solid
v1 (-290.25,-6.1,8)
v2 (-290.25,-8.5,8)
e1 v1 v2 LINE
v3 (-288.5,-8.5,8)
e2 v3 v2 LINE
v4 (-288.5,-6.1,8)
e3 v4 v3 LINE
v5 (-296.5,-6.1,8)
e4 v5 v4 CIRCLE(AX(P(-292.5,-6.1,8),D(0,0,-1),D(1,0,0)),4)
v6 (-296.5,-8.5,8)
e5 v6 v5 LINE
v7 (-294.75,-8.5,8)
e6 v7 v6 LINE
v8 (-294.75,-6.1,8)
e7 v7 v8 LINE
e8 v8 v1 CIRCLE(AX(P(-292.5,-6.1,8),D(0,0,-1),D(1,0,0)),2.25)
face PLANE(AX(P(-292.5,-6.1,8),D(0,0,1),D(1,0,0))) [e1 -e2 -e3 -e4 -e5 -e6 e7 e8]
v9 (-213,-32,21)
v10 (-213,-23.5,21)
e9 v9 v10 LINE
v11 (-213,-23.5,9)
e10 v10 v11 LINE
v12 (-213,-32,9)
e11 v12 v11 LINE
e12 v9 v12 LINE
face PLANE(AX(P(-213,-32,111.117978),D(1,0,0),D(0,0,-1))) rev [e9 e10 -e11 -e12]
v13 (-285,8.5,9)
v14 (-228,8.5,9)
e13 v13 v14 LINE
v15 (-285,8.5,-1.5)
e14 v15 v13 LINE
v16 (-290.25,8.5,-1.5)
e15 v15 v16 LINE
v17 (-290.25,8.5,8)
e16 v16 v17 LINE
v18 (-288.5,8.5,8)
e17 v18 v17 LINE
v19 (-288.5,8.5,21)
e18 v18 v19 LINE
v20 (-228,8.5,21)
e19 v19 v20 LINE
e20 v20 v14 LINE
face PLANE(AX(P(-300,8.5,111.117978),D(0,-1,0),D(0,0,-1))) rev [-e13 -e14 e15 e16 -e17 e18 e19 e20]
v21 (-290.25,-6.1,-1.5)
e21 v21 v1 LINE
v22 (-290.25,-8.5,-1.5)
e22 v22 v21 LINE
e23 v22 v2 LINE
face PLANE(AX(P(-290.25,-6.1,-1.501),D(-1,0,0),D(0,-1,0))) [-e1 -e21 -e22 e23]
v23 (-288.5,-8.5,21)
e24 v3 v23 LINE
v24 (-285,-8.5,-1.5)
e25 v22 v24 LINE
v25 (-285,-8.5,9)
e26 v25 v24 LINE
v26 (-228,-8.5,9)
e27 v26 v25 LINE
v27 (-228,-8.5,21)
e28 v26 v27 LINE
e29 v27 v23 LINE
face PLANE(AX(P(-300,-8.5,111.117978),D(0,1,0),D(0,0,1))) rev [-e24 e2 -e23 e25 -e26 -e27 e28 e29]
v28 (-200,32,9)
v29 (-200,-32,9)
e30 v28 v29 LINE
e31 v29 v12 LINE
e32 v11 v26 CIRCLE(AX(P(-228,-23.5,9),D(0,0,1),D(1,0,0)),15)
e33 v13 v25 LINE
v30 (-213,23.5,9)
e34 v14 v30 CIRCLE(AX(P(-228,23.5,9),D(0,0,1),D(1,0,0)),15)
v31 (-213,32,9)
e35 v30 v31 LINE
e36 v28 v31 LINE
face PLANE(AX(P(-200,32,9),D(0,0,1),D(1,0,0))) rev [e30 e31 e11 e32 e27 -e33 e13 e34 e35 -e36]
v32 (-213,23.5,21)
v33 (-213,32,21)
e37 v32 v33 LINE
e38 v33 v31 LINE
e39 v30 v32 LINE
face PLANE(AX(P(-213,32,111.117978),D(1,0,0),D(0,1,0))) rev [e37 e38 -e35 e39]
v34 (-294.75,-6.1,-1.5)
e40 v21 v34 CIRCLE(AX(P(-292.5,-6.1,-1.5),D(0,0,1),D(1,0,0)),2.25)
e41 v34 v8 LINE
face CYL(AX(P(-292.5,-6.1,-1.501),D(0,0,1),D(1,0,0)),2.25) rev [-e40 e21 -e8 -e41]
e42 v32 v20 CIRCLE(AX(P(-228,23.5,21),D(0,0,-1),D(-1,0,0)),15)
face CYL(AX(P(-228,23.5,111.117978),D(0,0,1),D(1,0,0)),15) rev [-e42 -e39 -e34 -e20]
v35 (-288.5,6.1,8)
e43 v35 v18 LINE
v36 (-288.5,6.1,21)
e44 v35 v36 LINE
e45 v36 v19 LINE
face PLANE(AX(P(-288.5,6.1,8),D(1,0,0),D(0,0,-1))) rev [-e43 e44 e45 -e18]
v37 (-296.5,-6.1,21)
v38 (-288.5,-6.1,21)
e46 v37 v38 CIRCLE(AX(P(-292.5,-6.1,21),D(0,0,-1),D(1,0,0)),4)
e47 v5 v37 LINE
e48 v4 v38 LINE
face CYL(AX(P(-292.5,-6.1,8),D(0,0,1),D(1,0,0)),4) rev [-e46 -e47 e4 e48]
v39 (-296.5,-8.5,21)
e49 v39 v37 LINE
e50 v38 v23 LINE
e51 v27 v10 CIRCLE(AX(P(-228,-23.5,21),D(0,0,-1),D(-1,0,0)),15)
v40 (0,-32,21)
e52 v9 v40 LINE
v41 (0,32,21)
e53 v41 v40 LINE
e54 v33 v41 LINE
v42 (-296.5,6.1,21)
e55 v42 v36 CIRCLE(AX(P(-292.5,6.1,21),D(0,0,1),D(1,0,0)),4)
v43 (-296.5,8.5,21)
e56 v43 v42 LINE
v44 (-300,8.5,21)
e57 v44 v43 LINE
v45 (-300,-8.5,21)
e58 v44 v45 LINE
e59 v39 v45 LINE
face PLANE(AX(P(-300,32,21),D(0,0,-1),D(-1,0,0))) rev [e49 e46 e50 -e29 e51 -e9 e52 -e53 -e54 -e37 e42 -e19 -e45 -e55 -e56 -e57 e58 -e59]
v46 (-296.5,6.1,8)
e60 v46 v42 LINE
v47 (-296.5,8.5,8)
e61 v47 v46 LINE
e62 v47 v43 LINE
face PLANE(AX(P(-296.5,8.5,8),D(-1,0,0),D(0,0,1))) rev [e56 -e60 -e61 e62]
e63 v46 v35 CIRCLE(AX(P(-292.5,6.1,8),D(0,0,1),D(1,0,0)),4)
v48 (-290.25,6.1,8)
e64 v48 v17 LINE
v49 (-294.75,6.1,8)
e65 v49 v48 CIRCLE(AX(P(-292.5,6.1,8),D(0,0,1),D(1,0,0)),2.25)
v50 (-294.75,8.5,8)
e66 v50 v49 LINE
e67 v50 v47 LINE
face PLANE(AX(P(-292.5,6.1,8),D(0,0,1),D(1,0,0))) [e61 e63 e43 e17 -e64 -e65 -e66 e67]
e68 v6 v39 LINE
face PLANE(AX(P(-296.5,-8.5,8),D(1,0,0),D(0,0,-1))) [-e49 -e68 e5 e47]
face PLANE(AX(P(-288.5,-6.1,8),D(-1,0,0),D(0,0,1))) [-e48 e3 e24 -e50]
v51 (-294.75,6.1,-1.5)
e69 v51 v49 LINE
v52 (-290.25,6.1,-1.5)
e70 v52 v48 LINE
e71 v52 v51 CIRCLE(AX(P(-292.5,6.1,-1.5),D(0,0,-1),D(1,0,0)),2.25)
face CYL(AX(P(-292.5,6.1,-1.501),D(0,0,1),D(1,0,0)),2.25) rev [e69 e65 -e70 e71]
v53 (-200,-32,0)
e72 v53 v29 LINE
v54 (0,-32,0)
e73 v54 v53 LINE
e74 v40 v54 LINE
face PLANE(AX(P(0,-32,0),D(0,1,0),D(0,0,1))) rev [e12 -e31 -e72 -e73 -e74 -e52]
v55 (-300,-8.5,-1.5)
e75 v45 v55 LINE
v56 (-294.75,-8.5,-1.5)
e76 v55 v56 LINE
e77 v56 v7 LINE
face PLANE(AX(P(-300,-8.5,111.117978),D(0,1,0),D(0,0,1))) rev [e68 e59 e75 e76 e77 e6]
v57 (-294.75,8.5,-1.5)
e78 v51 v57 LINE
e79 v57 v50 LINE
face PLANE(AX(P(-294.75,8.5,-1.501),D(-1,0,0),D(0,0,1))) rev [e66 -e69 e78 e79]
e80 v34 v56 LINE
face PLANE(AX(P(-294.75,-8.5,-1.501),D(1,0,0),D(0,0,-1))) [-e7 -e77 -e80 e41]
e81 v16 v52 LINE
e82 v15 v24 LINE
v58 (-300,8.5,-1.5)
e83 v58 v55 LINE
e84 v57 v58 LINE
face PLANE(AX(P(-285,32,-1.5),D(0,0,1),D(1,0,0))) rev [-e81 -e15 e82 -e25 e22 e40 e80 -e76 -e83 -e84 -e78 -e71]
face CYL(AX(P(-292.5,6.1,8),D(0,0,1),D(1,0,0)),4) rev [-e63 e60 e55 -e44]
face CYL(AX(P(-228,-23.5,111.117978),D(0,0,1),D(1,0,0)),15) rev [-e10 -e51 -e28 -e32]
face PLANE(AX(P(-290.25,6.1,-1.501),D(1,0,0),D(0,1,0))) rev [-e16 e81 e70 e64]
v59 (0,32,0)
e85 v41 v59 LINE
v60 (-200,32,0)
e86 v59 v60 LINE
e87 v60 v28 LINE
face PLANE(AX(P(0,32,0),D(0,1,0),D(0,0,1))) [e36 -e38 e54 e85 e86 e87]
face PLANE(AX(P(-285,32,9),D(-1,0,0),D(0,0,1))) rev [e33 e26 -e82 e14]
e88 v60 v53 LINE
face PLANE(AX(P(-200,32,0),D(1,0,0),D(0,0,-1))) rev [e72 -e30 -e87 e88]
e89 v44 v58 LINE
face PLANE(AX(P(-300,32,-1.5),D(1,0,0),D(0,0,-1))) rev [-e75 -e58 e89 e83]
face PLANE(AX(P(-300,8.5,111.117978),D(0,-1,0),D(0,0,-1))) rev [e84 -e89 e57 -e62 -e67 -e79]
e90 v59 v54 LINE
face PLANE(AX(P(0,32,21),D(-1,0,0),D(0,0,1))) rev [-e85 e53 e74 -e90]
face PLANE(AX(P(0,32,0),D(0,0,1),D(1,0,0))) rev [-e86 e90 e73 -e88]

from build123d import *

# Parameters (mm, degrees)
EXTRUDE_1_DEPTH     = 32
SKETCH_2_W          = 87
SKETCH_2_H          = 23.5
CUT_EXTRUDE_1_DEPTH = 22.5
FILLET_1_R          = 15
CUT_EXTRUDE_2_DEPTH = 13
CUT_EXTRUDE_3_REACH = 303.982


with BuildPart() as part:
    # 草图1 → 凸台-拉伸1 (new, symmetric)
    with BuildSketch(Plane(origin=(0, 0, 0), x_dir=(1, 0, 0), z_dir=(0, 1, 0))):
        Polygon((0, 0), (-200, 0), (-200, -9), (-285, -9), (-285, 1.5), (-300, 1.5), (-300, -21), (0, -21), align=None)
    extrude(amount=EXTRUDE_1_DEPTH, both=True)

    # 草图2 → 切除-拉伸1 (cut)
    with BuildSketch(Plane(origin=(0, 0, -1.5), x_dir=(-1, 0, 0), z_dir=(0, 0, -1))):
        with Locations((256.5, -20.25)):
            Rectangle(SKETCH_2_W, SKETCH_2_H)
        with Locations((256.5, 20.25)):
            Rectangle(SKETCH_2_W, SKETCH_2_H)
    extrude(amount=-CUT_EXTRUDE_1_DEPTH, mode=Mode.SUBTRACT)

    # 圆角1
    fillet_1_edges = [part.edges().sort_by_distance(p)[0] for p in [
        (-213, -8.5, 15),
        (-213, 8.5, 15),
    ]]
    fillet(fillet_1_edges, radius=FILLET_1_R)

    # 草图7 → 切除-拉伸2 (cut)
    with BuildSketch(Plane.XY.offset(21)):
        with BuildLine():
            Line((-296.5, 8.5), (-296.5, 6.1))
            ThreePointArc((-296.5, 6.1), (-292.5, 2.1), (-288.5, 6.1))
            Line((-288.5, 6.1), (-288.5, 8.5))
            Line((-288.5, 8.5), (-296.5, 8.5))
        make_face()
    cut_extrude_2 = extrude(amount=-CUT_EXTRUDE_2_DEPTH, mode=Mode.SUBTRACT)

    # 草图8 → 切除-拉伸3 (cut, up to next)
    with BuildSketch(Plane.XY.offset(8), mode=Mode.PRIVATE) as cut_extrude_3_sk1:
        with BuildLine():
            Line((-290.25, 6.1), (-290.25, 8.5))
            Line((-290.25, 8.5), (-294.75, 8.5))
            Line((-294.75, 8.5), (-294.75, 6.1))
            ThreePointArc((-294.75, 6.1), (-292.5, 3.85), (-290.25, 6.1))
        make_face()
    cut_extrude_3_tool1 = extrude(cut_extrude_3_sk1.sketch, amount=-CUT_EXTRUDE_3_REACH, mode=Mode.PRIVATE) & part.part
    cut_extrude_3 = cut_extrude_3_tool1.solids().sort_by_distance((-292.5, 6.386167, 8))[0]
    add(cut_extrude_3, mode=Mode.SUBTRACT)

    # 镜向1: 切除-拉伸2, 切除-拉伸3 across plane
    add(cut_extrude_2.mirror(Plane.ZX), mode=Mode.SUBTRACT)
    add(cut_extrude_3.mirror(Plane.ZX), mode=Mode.SUBTRACT)


solid = part.part
